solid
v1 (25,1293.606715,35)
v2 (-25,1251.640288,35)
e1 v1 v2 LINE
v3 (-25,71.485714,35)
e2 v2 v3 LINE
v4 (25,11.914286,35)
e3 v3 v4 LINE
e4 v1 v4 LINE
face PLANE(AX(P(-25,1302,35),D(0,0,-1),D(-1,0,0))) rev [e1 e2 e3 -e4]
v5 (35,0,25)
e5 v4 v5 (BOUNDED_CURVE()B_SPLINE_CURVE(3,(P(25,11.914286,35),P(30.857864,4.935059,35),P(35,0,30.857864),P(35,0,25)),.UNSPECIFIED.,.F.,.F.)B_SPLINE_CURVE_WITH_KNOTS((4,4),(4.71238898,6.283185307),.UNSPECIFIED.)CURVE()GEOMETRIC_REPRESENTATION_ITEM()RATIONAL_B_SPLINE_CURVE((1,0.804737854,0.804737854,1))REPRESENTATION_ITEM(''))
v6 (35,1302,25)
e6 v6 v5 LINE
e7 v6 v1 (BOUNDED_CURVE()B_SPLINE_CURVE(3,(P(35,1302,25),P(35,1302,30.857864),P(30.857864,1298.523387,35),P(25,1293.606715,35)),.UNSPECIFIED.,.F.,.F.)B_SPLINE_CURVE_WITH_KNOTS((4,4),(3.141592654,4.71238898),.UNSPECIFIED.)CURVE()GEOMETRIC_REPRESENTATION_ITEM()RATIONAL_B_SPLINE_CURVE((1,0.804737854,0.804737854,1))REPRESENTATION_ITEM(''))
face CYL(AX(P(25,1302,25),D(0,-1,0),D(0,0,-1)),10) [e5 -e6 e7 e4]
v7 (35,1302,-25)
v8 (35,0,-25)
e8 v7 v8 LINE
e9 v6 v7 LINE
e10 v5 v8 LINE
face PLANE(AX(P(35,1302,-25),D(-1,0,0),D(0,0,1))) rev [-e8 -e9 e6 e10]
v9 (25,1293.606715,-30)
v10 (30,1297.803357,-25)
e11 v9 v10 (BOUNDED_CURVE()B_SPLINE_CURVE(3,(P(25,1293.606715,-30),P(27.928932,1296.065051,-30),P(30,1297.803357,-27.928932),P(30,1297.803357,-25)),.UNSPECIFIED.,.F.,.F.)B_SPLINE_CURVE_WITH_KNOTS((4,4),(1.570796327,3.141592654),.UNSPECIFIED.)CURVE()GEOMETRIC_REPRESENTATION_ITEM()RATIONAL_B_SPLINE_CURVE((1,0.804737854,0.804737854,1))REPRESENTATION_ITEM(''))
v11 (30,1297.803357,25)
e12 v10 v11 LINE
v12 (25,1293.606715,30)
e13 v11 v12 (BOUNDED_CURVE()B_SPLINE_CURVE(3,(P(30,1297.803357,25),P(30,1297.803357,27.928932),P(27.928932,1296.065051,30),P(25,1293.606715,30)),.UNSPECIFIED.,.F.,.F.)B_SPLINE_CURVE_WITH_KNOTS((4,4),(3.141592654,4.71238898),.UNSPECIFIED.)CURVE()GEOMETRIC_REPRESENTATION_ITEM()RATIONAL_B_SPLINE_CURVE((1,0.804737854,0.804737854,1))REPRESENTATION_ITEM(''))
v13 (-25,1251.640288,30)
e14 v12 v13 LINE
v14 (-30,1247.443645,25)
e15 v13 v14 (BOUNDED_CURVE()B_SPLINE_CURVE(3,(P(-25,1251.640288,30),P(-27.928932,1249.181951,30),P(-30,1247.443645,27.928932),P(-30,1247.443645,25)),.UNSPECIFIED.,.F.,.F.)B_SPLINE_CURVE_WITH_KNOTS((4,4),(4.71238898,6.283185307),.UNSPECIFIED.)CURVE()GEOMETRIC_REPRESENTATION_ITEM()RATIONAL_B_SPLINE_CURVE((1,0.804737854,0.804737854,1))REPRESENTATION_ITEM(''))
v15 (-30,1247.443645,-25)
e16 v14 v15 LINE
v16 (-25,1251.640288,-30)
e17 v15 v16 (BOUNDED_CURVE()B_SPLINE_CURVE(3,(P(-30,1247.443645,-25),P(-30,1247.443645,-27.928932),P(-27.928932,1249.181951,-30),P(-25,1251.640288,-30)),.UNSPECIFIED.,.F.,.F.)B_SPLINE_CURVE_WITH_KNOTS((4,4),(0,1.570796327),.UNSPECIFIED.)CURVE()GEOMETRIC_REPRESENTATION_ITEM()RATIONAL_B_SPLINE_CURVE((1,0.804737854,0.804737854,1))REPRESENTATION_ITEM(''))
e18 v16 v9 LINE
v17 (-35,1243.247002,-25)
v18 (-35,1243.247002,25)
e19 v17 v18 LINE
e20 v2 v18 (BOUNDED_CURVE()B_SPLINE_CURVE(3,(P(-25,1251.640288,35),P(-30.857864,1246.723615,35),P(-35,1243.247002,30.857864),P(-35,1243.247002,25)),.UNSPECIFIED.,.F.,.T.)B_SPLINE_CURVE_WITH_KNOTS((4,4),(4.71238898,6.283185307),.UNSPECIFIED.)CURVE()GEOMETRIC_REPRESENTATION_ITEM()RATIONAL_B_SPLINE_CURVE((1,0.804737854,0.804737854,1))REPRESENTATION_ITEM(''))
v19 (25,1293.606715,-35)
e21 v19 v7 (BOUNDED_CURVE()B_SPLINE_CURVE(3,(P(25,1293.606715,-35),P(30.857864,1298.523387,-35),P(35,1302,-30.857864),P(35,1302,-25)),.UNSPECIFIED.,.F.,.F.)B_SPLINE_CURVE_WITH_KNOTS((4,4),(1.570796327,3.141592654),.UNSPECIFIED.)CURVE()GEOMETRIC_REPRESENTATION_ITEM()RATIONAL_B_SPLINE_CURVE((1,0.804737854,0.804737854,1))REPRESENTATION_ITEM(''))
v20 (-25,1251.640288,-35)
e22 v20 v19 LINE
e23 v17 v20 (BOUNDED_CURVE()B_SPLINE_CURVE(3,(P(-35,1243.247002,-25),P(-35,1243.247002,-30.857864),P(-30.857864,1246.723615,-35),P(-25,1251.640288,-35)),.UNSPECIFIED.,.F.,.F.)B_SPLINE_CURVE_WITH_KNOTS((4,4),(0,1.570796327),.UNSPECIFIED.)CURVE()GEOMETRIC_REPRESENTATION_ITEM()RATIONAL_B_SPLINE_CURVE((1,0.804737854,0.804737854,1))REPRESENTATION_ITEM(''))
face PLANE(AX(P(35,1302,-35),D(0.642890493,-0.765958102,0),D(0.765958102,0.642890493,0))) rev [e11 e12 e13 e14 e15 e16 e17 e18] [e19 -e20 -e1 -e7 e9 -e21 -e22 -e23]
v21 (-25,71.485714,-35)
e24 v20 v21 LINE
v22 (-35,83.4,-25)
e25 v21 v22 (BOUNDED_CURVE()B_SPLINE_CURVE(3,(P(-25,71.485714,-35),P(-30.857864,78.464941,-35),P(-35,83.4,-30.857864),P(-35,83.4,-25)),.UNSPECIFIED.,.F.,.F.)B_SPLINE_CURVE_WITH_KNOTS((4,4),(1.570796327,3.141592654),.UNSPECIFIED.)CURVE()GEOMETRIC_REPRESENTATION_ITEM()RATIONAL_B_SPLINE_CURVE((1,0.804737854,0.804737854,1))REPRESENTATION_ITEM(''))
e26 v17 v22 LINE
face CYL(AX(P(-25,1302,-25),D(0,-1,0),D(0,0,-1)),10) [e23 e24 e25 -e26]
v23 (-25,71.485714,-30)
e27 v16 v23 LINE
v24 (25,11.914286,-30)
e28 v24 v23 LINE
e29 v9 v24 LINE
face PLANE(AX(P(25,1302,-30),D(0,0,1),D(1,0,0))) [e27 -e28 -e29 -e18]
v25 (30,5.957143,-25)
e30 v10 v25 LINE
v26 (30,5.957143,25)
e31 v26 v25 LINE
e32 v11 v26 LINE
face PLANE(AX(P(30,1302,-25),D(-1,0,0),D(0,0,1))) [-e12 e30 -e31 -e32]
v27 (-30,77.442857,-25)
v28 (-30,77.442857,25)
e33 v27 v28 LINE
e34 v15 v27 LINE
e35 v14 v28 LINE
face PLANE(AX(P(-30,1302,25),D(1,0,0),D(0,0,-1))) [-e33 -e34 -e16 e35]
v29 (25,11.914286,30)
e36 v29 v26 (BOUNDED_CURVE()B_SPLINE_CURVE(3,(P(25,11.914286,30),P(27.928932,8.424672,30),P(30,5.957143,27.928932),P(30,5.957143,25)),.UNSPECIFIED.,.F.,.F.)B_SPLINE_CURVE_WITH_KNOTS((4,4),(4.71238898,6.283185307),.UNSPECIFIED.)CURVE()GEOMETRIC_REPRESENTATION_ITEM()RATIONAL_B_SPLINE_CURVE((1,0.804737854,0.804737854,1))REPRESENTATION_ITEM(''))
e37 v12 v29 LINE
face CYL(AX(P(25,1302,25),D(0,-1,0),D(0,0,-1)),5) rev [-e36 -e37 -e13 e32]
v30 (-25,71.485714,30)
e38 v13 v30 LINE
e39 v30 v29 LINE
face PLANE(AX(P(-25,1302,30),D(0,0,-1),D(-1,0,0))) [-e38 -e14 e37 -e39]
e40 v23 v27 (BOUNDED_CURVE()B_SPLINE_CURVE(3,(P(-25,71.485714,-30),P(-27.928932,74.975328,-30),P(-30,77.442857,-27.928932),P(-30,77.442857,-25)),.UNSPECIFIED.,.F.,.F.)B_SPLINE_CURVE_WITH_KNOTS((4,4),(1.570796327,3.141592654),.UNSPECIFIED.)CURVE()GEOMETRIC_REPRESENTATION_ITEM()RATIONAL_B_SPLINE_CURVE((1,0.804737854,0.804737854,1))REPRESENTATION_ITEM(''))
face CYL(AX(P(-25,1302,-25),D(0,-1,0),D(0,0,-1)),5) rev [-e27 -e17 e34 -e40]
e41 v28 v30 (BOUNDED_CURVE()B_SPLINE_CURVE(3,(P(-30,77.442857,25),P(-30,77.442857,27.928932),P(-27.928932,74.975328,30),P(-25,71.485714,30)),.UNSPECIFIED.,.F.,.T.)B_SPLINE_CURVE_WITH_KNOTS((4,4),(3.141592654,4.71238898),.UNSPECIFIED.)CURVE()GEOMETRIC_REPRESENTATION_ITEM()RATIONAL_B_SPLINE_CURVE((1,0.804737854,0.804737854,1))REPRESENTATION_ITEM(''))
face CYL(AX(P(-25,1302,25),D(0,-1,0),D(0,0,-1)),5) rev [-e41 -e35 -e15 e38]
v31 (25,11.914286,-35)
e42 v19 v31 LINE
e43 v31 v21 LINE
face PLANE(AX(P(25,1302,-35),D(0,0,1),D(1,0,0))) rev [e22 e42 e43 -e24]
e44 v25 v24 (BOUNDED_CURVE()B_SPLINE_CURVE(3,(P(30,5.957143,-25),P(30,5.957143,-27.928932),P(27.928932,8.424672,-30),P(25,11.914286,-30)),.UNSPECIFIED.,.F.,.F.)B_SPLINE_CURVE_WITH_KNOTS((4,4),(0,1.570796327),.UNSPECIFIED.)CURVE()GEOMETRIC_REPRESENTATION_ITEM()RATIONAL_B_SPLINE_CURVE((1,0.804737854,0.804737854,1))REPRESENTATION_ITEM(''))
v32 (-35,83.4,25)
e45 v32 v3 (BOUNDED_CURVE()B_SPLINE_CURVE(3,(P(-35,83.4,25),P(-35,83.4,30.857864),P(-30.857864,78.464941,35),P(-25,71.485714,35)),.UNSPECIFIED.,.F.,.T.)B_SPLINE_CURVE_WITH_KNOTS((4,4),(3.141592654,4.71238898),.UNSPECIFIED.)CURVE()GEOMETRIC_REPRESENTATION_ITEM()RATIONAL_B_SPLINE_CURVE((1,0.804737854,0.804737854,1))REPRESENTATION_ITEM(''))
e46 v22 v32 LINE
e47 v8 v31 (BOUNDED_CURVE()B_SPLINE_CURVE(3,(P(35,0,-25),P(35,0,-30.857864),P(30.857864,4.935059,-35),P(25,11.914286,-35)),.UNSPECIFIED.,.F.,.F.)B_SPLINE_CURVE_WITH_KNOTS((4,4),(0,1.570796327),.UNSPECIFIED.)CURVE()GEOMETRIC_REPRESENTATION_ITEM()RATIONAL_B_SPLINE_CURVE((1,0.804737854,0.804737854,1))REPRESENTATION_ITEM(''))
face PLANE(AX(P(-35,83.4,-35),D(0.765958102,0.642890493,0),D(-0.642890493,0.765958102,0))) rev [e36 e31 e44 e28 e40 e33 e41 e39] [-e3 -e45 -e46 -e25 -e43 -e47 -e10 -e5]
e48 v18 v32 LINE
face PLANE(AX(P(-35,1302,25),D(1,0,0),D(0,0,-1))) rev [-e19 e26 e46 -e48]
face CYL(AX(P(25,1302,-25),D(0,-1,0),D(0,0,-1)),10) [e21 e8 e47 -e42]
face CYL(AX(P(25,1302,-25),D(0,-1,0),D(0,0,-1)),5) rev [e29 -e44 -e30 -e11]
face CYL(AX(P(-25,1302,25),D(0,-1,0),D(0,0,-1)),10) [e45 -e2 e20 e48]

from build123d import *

# Parameters (mm, degrees)
FEATURE_19_WELDMEMBERFEAT_4_MORE_IN_5_DEPTH = 1302
CUT_EXTRUDE1_DEPTH                          = 1305.350029708
CUT_EXTRUDE1_DEPTH_BACK                     = 1305.350029708


with BuildPart() as part:
    # Sketch1 → feature 19 (WeldMemberFeat) (+4 more in 5 files) Cold-formed Hollow Structural Square Steel(gb t6728-2002) 70×70×5(1) (new body)
    with BuildSketch(Plane(origin=(0, 0, 0), x_dir=(-1, 0, 0), z_dir=(0, 1, 0))):
        with BuildLine():
            Line((-25, -35), (25, -35))
            ThreePointArc((25, -35), (32.071067812, -32.071067812), (35, -25))
            Line((35, -25), (35, 25))
            ThreePointArc((35, 25), (32.071067812, 32.071067812), (25, 35))
            Line((25, 35), (-25, 35))
            ThreePointArc((-25, 35), (-32.071067812, 32.071067812), (-35, 25))
            Line((-35, 25), (-35, -25))
            ThreePointArc((-35, -25), (-32.071067812, -32.071067812), (-25, -35))
        make_face()
        with BuildLine():
            Line((-25, -30), (25, -30))
            ThreePointArc((25, -30), (28.535533906, -28.535533906), (30, -25))
            Line((30, -25), (30, 25))
            ThreePointArc((30, 25), (28.535533906, 28.535533906), (25, 30))
            Line((25, 30), (-25, 30))
            ThreePointArc((-25, 30), (-28.535533906, 28.535533906), (-30, 25))
            Line((-30, 25), (-30, -25))
            ThreePointArc((-30, -25), (-28.535533906, -28.535533906), (-25, -30))
        make_face(mode=Mode.SUBTRACT)
    extrude(amount=FEATURE_19_WELDMEMBERFEAT_4_MORE_IN_5_DEPTH)

    # 0:feat:20/0 feature 20/0 (ProfileFeature) (+11 more in 7 files) Sketch2 → Cut-Extrude1 (cut, two sides: drawn at the far end of the back side and taken through both)
    with BuildSketch(Plane.XY.offset(35).offset(-CUT_EXTRUDE1_DEPTH_BACK)):
        Polygon((35, 1302), (-35, 1243.247002398), (-35, 1302), align=None)
        Polygon((-35, 83.4), (35, 0), (-35, 0), align=None)
    extrude(amount=CUT_EXTRUDE1_DEPTH + CUT_EXTRUDE1_DEPTH_BACK, mode=Mode.SUBTRACT)


solid = part.part
